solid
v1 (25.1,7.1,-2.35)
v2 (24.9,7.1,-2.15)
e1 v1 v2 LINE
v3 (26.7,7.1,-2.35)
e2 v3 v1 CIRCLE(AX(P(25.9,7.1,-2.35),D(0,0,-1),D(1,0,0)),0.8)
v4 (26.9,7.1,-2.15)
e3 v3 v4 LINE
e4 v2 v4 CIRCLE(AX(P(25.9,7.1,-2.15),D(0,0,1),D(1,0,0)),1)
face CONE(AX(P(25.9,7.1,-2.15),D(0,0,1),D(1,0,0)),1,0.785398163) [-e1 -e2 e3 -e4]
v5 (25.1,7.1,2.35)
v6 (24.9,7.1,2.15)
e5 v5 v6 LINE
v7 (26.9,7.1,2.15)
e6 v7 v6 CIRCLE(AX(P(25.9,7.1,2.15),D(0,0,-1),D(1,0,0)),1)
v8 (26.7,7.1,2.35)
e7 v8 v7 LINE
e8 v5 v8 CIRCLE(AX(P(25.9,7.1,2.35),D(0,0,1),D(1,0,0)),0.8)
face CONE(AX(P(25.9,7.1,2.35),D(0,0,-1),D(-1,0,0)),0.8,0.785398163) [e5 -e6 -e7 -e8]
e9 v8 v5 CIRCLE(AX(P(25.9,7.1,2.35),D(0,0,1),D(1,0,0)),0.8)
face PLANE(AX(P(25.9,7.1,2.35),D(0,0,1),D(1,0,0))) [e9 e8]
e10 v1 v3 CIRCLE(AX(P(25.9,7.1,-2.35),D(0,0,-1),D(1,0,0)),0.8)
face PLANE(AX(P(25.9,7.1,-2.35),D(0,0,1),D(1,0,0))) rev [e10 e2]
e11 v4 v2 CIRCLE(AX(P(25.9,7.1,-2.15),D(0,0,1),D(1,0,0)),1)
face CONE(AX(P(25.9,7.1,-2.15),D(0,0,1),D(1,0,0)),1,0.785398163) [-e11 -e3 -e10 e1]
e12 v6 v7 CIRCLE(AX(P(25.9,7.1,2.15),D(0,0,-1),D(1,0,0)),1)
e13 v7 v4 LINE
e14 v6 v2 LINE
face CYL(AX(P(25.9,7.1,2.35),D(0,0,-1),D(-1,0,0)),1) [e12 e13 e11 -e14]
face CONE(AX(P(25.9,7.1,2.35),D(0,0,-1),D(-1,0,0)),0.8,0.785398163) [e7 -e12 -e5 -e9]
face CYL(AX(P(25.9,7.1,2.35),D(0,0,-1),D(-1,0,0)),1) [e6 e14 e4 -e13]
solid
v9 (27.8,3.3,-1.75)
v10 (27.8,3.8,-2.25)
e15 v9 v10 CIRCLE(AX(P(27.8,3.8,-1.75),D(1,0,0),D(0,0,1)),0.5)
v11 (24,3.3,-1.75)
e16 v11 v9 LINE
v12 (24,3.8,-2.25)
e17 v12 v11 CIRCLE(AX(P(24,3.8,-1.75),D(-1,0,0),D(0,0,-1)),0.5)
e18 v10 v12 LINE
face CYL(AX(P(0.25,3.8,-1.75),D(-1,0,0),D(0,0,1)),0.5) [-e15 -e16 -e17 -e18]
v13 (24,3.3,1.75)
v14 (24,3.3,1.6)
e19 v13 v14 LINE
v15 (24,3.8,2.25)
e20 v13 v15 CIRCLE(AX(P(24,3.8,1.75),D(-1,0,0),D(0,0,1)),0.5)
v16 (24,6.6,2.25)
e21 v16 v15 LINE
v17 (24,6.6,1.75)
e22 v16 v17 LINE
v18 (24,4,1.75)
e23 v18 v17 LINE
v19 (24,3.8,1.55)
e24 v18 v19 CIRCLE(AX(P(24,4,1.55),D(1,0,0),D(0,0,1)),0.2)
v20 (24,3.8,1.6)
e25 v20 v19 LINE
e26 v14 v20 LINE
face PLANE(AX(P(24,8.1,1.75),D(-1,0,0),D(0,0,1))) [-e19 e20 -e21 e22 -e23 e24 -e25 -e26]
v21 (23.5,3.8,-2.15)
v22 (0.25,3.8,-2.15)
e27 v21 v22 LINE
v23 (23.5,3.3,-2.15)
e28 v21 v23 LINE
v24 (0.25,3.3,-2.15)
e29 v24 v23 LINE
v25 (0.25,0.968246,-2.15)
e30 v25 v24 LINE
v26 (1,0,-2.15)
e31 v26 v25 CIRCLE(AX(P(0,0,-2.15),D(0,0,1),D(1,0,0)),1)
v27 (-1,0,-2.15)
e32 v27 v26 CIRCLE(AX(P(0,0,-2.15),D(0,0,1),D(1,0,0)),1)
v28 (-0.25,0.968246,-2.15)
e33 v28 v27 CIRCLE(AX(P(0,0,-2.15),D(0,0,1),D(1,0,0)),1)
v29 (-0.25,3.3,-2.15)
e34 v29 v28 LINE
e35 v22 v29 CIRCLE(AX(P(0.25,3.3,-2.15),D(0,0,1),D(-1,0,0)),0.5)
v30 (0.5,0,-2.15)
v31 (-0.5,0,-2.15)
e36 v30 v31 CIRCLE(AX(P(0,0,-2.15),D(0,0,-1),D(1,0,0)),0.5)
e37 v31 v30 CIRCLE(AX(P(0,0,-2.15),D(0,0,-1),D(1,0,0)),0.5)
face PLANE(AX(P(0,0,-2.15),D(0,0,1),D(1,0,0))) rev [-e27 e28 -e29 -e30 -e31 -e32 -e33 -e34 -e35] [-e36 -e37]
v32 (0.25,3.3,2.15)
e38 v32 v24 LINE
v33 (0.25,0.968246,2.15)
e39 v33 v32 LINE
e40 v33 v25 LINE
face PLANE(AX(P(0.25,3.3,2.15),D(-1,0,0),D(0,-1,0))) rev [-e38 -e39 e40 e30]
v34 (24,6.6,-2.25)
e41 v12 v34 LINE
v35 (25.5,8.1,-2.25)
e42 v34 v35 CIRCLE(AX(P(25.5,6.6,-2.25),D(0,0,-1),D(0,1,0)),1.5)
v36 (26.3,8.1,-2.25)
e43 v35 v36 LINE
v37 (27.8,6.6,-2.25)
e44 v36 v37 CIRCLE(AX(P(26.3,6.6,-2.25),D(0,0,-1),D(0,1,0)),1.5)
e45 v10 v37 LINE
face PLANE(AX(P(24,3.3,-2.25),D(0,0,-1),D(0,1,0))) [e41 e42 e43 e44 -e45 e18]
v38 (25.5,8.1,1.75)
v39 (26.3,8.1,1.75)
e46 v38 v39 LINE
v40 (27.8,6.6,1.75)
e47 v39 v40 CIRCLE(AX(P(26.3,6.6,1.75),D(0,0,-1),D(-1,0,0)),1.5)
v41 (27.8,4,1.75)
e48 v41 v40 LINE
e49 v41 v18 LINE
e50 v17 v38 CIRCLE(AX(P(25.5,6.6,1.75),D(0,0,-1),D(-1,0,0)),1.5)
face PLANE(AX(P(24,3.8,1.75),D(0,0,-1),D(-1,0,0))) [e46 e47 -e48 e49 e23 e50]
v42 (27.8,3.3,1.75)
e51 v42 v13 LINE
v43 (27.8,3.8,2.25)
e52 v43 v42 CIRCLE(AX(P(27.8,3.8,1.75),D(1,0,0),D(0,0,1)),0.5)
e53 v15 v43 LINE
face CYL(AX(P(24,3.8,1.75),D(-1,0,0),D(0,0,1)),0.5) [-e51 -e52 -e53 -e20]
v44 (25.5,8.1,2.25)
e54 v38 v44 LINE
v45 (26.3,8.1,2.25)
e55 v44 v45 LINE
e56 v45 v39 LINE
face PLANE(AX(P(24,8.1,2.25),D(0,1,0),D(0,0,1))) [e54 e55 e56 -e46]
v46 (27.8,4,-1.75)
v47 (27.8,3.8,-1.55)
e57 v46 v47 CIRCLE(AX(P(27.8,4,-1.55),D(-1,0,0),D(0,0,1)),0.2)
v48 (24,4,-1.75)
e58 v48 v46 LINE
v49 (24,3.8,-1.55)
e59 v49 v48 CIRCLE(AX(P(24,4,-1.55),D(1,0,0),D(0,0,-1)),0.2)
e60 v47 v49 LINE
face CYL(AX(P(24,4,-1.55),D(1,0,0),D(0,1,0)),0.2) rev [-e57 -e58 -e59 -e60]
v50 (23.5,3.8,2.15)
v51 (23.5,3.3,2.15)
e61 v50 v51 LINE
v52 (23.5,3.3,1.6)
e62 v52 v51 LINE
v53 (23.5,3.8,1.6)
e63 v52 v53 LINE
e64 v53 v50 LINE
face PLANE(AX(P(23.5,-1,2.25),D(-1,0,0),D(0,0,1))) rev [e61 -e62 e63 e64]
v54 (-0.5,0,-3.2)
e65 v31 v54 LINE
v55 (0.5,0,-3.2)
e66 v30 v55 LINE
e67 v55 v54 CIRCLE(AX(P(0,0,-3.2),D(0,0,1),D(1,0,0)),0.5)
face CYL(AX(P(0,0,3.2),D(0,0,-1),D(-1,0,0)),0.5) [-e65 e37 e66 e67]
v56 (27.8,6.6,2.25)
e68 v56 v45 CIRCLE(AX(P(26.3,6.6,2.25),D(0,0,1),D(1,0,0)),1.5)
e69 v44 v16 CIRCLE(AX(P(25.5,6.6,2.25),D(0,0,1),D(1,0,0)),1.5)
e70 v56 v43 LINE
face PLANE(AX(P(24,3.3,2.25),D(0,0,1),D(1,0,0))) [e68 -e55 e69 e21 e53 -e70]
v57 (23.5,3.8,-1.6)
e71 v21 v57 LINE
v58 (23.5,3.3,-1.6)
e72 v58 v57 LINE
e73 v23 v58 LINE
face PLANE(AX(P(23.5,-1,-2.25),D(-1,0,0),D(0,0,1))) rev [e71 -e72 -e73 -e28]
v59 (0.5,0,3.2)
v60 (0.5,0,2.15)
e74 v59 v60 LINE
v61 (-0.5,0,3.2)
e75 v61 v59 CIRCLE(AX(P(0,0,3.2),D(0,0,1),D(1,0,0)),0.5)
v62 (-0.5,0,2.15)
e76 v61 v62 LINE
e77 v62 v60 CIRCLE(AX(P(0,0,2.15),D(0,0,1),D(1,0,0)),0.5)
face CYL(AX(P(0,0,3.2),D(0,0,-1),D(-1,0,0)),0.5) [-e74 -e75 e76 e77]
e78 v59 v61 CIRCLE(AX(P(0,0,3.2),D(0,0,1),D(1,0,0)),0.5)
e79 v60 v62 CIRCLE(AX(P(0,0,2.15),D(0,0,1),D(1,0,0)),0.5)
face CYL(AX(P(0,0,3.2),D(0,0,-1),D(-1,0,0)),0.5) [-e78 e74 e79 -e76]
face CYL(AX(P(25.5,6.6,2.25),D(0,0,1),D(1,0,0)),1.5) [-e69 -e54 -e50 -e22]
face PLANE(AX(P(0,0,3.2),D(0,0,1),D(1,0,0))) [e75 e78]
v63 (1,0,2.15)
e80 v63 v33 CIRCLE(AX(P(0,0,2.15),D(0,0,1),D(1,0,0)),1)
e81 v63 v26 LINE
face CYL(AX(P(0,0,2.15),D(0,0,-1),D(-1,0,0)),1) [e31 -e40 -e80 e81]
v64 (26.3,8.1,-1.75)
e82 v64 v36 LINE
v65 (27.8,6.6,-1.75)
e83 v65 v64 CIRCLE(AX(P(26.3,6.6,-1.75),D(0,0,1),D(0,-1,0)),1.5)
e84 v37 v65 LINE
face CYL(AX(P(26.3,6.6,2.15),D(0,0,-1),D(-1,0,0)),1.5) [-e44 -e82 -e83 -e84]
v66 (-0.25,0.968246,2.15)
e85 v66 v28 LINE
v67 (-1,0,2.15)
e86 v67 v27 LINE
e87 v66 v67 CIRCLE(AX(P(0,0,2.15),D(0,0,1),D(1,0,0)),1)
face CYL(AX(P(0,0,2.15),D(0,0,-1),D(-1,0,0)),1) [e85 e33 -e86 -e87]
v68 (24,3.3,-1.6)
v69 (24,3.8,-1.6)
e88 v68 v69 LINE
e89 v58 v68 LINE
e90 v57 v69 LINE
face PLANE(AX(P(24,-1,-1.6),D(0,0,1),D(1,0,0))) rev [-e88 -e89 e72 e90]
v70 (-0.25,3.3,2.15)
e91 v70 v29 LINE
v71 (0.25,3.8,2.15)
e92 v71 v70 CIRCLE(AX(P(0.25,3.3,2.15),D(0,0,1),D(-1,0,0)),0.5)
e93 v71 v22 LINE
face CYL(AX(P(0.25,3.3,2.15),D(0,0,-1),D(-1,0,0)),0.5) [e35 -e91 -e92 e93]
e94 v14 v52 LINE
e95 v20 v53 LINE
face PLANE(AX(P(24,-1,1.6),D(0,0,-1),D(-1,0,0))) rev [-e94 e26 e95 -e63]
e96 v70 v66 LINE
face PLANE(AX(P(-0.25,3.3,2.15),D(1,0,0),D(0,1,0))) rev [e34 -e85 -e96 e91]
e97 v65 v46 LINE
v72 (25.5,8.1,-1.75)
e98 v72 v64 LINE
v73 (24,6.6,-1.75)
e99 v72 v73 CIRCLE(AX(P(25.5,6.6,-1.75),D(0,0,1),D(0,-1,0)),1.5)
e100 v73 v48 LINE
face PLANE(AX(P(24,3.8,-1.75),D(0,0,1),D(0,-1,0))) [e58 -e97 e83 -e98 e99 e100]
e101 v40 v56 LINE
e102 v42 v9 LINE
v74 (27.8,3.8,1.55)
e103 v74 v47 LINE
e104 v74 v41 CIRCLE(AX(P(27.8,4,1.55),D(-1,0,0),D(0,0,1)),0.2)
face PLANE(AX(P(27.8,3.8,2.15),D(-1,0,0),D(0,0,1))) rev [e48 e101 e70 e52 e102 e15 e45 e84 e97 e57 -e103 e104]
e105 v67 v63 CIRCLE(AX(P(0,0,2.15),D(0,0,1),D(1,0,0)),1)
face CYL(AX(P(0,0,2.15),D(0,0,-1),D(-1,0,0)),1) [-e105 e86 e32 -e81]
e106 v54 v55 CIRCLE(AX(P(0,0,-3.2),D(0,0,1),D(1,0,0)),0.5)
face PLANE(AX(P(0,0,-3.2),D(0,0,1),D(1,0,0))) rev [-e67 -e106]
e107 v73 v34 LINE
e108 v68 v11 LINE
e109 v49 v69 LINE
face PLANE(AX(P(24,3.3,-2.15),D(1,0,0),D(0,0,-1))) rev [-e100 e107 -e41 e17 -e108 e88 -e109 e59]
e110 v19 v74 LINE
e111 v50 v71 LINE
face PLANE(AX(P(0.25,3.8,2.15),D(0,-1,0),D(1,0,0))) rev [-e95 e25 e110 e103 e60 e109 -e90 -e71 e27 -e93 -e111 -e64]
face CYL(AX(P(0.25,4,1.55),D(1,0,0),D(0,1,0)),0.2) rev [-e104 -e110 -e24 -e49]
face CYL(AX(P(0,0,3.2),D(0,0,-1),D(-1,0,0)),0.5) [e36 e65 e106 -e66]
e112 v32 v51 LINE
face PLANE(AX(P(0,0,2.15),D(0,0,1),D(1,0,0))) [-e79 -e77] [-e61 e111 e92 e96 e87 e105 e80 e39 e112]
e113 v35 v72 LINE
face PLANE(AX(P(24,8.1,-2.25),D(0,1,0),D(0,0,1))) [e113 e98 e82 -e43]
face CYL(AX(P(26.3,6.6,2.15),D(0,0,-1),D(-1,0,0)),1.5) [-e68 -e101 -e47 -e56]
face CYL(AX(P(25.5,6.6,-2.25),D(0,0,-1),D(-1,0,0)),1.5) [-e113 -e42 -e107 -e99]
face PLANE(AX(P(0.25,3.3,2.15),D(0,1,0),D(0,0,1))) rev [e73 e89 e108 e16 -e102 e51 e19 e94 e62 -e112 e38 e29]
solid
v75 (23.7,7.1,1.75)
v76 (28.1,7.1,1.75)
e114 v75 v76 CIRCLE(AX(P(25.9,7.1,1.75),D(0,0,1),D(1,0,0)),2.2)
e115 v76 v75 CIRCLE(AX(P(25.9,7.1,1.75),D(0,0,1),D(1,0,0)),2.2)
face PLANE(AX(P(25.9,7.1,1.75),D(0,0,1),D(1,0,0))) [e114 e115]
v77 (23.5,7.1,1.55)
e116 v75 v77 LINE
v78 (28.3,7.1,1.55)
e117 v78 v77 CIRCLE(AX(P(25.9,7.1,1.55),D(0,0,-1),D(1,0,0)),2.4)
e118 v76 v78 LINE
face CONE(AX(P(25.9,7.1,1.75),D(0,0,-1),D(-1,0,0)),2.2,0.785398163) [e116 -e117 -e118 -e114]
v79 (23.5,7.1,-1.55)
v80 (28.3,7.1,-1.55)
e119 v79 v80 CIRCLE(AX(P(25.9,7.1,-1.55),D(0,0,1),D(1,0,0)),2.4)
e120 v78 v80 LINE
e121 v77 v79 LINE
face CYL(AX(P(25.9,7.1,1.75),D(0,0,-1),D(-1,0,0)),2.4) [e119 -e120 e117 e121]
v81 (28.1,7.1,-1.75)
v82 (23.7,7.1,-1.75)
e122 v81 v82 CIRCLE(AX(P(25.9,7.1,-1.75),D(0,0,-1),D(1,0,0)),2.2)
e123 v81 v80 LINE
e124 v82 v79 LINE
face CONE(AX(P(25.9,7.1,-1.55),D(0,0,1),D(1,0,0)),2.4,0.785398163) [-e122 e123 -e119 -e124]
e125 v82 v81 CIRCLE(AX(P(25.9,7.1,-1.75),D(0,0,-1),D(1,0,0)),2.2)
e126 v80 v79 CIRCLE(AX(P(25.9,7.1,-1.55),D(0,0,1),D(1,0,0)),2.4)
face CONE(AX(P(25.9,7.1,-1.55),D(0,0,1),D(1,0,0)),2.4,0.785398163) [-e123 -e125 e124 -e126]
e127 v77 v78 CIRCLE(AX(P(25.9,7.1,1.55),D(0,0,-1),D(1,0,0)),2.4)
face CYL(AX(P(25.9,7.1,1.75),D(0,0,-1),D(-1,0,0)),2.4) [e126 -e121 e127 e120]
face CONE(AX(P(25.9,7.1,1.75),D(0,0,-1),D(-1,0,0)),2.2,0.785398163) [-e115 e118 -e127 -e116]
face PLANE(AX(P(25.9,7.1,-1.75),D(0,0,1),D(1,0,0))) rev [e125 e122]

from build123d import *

# Parameters (mm, degrees)
SKETCH_1_R          = 0.5
EXTRUDE_1_DEPTH     = 2.15
SKETCH_2_R          = 0.5
EXTRUDE_2_DEPTH     = 3.2
EXTRUDE_3_DEPTH     = 3.8
FILLET_2_R          = 0.2
SKETCH_4_W          = 0.5
SKETCH_4_H          = 0.65
CUT_EXTRUDE_1_DEPTH = 29.392252464
FILLET_3_R          = 0.5
SKETCH_5_R          = 1
EXTRUDE_4_DEPTH     = 2.35
CHAMFER_1_SIZE      = 0.2
SKETCH_6_R          = 2.4
EXTRUDE_5_DEPTH     = 1.75
CHAMFER_2_SIZE      = 0.2
FILLET_4_R          = 1.5


with BuildPart() as part:
    # 草图1 → 凸台-拉伸1 (new, symmetric)
    with BuildSketch(Plane.XY):
        with BuildLine():
            Line((-0.25, 3.3), (-0.25, 0.968245837))
            ThreePointArc((-0.25, 0.968245837), (0, -1), (0.25, 0.968245837))
            Line((0.25, 0.968245837), (0.25, 3.3))
            Line((0.25, 3.3), (27.8, 3.3))
            Line((27.8, 3.3), (27.8, 3.8))
            Line((27.8, 3.8), (0.25, 3.8))
            ThreePointArc((0.25, 3.8), (-0.103553391, 3.653553391), (-0.25, 3.3))
        make_face()
        Circle(SKETCH_1_R, mode=Mode.SUBTRACT)
    extrude(amount=EXTRUDE_1_DEPTH, both=True)

    # 草图2 → 凸台-拉伸2 (add, symmetric)
    with BuildSketch(Plane.XY):
        Circle(SKETCH_2_R)
    extrude(amount=EXTRUDE_2_DEPTH, both=True)

    # 草图3 → 凸台-拉伸3 (add)
    with BuildSketch(Plane(origin=(27.8, 0, 0), x_dir=(0, 0, -1), z_dir=(1, 0, 0))):
        Polygon((-2.15, 3.8), (-1.75, 3.8), (-1.75, 8.1), (-2.25, 8.1), (-2.25, 3.3), (-2.15, 3.3), align=None)
        Polygon((2.15, 3.3), (2.25, 3.3), (2.25, 8.1), (1.75, 8.1), (1.75, 3.8), (2.15, 3.8), align=None)
    extrude(amount=-EXTRUDE_3_DEPTH)

    # 圆角2
    fillet_2_edges = [part.edges().sort_by_distance(p)[0] for p in [
        (25.9, 3.8, -1.75),
        (25.9, 3.8, 1.75),
    ]]
    fillet(fillet_2_edges, radius=FILLET_2_R)

    # 草图4 → 切除-拉伸1 (cut, through all)
    with BuildSketch(Plane(origin=(0, 3.8, 0), x_dir=(1, 0, 0), z_dir=(0, 1, 0))):
        with Locations((23.75, -1.925)):
            Rectangle(SKETCH_4_W, SKETCH_4_H)
        with Locations((23.75, 1.925)):
            Rectangle(SKETCH_4_W, SKETCH_4_H)
    extrude(amount=-CUT_EXTRUDE_1_DEPTH, mode=Mode.SUBTRACT)

    # 圆角3
    fillet_3_edges = [part.edges().sort_by_distance(p)[0] for p in [
        (25.9, 3.3, -2.25),
        (25.9, 3.3, 2.25),
    ]]
    fillet(fillet_3_edges, radius=FILLET_3_R)

    # 圆角4
    fillet_4_edges = [part.edges().sort_by_distance(p)[0] for p in [
        (24, 8.1, -2),
        (27.8, 8.1, -2),
        (24, 8.1, 2),
        (27.8, 8.1, 2),
    ]]
    fillet(fillet_4_edges, radius=FILLET_4_R)


with BuildPart() as body_2:
    # 草图5 → 凸台-拉伸4 (new, symmetric)
    with BuildSketch(Plane.XY):
        with Locations(Location((25.9, 7.1, 0), (0, 0, 180))):
            Circle(SKETCH_5_R)
    extrude(amount=EXTRUDE_4_DEPTH, both=True)

    # 倒角1
    chamfer_1_edges = [body_2.edges().sort_by_distance(p)[0] for p in [
        (26.9, 7.1, -2.35),
        (26.9, 7.1, 2.35),
    ]]
    chamfer(chamfer_1_edges, length=CHAMFER_1_SIZE)


with BuildPart() as body_3:
    # 草图6 → 凸台-拉伸5 (new, symmetric)
    with BuildSketch(Plane.XY):
        with Locations((25.9, 7.1)):
            Circle(SKETCH_6_R)
    extrude(amount=EXTRUDE_5_DEPTH, both=True)

    # 倒角2
    chamfer_2_edges = [body_3.edges().sort_by_distance(p)[0] for p in [
        (23.5, 7.1, -1.75),
        (23.5, 7.1, 1.75),
    ]]
    chamfer(chamfer_2_edges, length=CHAMFER_2_SIZE)


solid = Compound([part.part, body_2.part, body_3.part])
